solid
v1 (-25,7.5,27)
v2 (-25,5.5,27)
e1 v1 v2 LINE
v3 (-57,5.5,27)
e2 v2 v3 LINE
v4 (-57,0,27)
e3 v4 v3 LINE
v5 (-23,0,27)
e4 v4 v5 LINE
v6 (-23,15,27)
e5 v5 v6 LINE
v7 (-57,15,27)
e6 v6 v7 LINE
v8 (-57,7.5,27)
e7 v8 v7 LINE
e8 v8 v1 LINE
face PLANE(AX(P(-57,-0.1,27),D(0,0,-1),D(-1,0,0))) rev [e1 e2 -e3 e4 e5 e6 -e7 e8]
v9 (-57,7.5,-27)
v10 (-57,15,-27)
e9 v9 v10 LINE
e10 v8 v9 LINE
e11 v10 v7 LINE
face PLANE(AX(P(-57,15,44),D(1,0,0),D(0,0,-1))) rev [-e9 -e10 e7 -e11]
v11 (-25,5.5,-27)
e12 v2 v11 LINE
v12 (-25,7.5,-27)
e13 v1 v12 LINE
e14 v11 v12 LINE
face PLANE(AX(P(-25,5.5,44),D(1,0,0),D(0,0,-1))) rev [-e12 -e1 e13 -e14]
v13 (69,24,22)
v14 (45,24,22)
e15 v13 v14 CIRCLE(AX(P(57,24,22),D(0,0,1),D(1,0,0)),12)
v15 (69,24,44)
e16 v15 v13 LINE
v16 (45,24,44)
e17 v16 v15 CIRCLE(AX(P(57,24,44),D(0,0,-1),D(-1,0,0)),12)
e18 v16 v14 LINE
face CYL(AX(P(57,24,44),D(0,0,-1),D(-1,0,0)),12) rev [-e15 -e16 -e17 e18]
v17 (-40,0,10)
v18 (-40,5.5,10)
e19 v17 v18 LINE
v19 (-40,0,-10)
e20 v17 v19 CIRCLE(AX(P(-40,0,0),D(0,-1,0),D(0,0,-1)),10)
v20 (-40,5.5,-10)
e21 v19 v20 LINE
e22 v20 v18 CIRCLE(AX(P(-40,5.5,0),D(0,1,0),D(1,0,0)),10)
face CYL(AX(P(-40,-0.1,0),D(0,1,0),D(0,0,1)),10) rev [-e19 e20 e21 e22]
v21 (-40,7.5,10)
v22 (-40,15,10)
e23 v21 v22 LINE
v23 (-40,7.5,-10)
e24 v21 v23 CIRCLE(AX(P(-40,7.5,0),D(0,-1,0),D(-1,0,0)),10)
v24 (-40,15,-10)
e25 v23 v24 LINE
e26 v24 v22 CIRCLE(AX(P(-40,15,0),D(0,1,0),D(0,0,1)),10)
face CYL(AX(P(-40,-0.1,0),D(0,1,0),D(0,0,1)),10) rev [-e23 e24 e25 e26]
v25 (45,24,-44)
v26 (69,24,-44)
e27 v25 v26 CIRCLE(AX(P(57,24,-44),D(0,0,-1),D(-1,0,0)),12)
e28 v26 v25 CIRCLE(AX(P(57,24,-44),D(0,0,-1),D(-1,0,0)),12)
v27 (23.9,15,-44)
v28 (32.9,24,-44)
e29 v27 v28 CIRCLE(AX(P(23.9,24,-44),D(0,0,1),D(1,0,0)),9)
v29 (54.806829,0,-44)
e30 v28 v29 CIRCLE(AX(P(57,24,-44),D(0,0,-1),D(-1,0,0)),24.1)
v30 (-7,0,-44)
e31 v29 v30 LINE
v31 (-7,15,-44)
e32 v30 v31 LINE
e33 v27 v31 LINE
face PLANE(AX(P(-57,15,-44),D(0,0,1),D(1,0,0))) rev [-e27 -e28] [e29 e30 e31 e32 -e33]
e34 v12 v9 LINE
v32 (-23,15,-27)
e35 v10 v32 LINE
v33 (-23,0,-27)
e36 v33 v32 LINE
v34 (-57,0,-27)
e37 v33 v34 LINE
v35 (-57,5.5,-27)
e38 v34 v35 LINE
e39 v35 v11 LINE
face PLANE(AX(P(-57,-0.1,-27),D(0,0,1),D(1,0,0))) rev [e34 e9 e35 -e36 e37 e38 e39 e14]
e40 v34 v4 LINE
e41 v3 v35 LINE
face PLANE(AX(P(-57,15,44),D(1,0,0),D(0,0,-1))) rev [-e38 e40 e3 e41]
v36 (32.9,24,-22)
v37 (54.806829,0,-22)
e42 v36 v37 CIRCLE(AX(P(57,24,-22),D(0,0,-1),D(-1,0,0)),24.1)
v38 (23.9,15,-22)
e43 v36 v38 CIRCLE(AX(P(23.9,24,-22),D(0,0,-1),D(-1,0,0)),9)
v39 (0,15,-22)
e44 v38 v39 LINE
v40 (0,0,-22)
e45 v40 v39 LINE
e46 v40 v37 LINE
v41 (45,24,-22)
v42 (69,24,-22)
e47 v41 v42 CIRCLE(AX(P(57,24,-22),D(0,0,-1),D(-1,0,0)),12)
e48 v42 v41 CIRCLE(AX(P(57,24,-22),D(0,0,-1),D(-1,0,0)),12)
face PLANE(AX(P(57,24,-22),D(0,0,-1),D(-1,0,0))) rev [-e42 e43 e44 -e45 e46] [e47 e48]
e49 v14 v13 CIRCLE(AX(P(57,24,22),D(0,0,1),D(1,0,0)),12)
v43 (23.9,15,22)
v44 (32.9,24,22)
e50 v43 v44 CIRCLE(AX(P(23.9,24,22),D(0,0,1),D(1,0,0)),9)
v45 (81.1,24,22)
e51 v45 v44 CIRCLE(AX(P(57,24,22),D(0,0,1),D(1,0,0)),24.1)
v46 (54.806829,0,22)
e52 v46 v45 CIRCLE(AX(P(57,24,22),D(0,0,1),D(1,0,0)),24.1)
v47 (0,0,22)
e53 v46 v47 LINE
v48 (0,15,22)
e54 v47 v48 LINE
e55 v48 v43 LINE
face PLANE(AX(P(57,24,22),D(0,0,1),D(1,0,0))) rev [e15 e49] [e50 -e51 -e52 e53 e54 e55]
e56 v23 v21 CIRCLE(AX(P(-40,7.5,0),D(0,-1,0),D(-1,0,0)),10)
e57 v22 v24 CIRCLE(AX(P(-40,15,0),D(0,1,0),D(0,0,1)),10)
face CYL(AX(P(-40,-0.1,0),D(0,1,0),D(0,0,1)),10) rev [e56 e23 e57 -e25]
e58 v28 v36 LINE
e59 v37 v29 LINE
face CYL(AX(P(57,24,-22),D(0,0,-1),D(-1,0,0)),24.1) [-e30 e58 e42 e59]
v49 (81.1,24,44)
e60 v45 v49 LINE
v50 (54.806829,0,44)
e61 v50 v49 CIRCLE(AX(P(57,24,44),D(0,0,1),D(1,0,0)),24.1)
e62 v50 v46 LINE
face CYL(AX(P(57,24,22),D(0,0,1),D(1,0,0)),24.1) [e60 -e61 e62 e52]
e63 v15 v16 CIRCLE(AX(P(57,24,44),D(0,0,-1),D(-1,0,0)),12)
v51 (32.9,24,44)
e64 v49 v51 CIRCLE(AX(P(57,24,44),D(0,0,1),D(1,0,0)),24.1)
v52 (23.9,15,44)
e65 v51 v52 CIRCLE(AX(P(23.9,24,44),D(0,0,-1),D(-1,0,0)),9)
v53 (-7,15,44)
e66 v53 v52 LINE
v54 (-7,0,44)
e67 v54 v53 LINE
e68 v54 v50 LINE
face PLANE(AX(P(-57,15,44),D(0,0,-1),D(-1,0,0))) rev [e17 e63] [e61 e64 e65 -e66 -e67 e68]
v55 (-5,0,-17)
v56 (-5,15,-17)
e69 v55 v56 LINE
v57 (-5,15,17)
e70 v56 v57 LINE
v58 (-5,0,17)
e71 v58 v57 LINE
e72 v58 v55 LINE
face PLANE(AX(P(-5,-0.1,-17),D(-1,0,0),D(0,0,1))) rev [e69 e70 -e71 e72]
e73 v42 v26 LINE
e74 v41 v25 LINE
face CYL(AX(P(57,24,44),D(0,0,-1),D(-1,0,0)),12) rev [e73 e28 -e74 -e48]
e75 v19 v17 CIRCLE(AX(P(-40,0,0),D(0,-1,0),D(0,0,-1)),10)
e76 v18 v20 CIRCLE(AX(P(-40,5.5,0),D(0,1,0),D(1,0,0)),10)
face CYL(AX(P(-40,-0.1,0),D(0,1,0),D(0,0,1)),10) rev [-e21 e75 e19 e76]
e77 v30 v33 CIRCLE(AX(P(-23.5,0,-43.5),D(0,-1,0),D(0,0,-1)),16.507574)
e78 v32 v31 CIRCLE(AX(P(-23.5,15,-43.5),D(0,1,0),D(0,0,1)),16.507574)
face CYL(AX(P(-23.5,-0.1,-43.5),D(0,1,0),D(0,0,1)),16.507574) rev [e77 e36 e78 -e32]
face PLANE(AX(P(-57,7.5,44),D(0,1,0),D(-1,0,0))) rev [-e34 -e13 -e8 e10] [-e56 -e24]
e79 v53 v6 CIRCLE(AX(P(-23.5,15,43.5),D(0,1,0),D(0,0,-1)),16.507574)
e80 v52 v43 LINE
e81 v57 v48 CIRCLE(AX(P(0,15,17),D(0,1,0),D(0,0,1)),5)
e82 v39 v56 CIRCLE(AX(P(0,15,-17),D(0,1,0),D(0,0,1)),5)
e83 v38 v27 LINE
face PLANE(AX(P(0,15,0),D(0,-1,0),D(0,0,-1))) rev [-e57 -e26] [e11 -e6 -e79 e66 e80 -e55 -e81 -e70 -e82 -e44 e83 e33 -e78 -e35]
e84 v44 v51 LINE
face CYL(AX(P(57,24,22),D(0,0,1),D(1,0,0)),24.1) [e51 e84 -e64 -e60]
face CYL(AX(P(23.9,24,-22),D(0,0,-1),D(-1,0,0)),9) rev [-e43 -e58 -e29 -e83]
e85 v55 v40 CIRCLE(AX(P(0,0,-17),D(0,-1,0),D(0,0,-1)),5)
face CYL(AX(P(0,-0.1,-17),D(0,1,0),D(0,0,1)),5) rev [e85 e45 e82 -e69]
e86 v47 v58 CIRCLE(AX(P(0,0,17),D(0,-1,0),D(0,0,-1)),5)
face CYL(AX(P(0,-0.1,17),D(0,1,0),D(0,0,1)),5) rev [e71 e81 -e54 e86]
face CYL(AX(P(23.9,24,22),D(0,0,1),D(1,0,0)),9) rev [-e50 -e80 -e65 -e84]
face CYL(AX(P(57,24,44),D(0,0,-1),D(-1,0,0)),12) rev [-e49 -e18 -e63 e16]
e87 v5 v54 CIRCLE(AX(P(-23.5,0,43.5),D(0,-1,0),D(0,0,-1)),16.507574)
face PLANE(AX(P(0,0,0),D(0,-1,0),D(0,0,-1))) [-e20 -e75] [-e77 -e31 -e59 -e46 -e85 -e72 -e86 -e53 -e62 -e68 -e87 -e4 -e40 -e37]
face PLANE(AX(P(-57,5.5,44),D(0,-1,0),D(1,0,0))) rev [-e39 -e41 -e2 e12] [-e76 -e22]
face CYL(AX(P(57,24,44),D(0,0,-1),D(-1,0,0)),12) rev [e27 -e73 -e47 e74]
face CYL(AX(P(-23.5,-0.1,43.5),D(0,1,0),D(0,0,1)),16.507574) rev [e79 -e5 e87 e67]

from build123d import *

# Parameters (mm, degrees)
BASE_PLATE_SKETCH_W               = 114
BASE_PLATE_SKETCH_H               = 88
BASE_PLATE_114X88X15_DEPTH        = 15
FORK_EYE_A_SKETCH_R               = 24.1
FORK_EYE_A_48_2_DEPTH             = 22
FORK_START                        = -22
FORK_EYE_B_SKETCH_R               = 24.1
FORK_EYE_B_48_2_DEPTH             = 22
EYE_BORE_SKETCH_R                 = 12
EYE_BORE_24_DEPTH                 = 129.976044287
FORK_FILLET_R9_R                  = 9
FORK_GAP_PROFILE_SKETCH_R         = 10
FORK_GAP_AND_CLAMP_HOLE_CUT_DEPTH = 99.024588752
CLAMP_SLIT_2MM_DEPTH              = 119.033130942
CLAMP_SLIT_2MM_DEPTH_BACK         = 119.033130942
CLAMP_SLIT_SKETCH_W               = 32
CLAMP_SLIT_SKETCH_H               = 2


with BuildPart() as part:
    # Base Plate Sketch → Base Plate 114x88x15 (new body)
    with BuildSketch(Plane(origin=(0, 0, 0), x_dir=(1, 0, 0), z_dir=(0, 1, 0))):
        Rectangle(BASE_PLATE_SKETCH_W, BASE_PLATE_SKETCH_H)
    extrude(amount=BASE_PLATE_114X88X15_DEPTH)

    # Fork Eye A Sketch → Fork Eye A Ø48.2 (add)
    with BuildSketch(Plane.XY.offset(44)):
        with Locations((57, 24)):
            Circle(FORK_EYE_A_SKETCH_R)
    extrude(amount=-FORK_EYE_A_48_2_DEPTH)

    # Fork Eye B Sketch → Fork Eye B Ø48.2 (add)
    with BuildSketch(Plane(origin=(0, 0, -44), x_dir=(-1, 0, 0), z_dir=(0, 0, -1)).offset(FORK_START)):
        with Locations((-57, 24)):
            Circle(FORK_EYE_B_SKETCH_R)
    extrude(amount=FORK_EYE_B_48_2_DEPTH)

    # Eye Bore Sketch → Eye Bore Ø24 (cut, through all)
    with BuildSketch(Plane(origin=(0, 0, -44), x_dir=(-1, 0, 0), z_dir=(0, 0, -1))):
        with Locations((-57, 24)):
            Circle(EYE_BORE_SKETCH_R)
    extrude(amount=-EYE_BORE_24_DEPTH, mode=Mode.SUBTRACT)

    # Fork Fillet R9
    fork_fillet_r9_edges = [part.edges().sort_by_distance(p)[0] for p in [
        (34.643569158, 15, 33),
        (34.643569158, 15, -33),
    ]]
    fillet(fork_fillet_r9_edges, radius=FORK_FILLET_R9_R)

    # Fork Gap Profile Sketch → Fork Gap and Clamp Hole Cut (cut, through all)
    with BuildSketch(Plane(origin=(0, 15, 0), x_dir=(1, 0, 0), z_dir=(0, 1, 0))):
        with Locations(Location((-40, 0, 0), (0, 0, 270))):
            Circle(FORK_GAP_PROFILE_SKETCH_R)
        with BuildLine():
            Line((57, 22), (0, 22))
            ThreePointArc((0, 22), (-3.535533906, 20.535533906), (-5, 17))
            Line((-5, 17), (-5, -17))
            ThreePointArc((-5, -17), (-3.535533906, -20.535533906), (0, -22))
            Line((0, -22), (57, -22))
            Line((57, -22), (57, 22))
        make_face()
        with BuildLine():
            Line((-57, 44), (-7, 44))
            ThreePointArc((-7, 44), (-11.47918472, 32.186291501), (-23, 27))
            Line((-23, 27), (-57, 27))
            Line((-57, 27), (-57, 44))
        make_face()
        with BuildLine():
            Line((-57, -44), (-7, -44))
            ThreePointArc((-7, -44), (-11.47918472, -32.186291501), (-23, -27))
            Line((-23, -27), (-57, -27))
            Line((-57, -27), (-57, -44))
        make_face()
    extrude(amount=-FORK_GAP_AND_CLAMP_HOLE_CUT_DEPTH, mode=Mode.SUBTRACT)

    # Clamp Slit Sketch → Clamp Slit 2mm (cut, two sides: drawn at the far end of the back side and taken through both)
    with BuildSketch(Plane(origin=(0, 0, -27), x_dir=(-1, 0, 0), z_dir=(0, 0, -1)).offset(-CLAMP_SLIT_2MM_DEPTH_BACK)):
        with Locations((41, 6.5)):
            Rectangle(CLAMP_SLIT_SKETCH_W, CLAMP_SLIT_SKETCH_H)
    extrude(amount=CLAMP_SLIT_2MM_DEPTH + CLAMP_SLIT_2MM_DEPTH_BACK, mode=Mode.SUBTRACT)


solid = part.part
